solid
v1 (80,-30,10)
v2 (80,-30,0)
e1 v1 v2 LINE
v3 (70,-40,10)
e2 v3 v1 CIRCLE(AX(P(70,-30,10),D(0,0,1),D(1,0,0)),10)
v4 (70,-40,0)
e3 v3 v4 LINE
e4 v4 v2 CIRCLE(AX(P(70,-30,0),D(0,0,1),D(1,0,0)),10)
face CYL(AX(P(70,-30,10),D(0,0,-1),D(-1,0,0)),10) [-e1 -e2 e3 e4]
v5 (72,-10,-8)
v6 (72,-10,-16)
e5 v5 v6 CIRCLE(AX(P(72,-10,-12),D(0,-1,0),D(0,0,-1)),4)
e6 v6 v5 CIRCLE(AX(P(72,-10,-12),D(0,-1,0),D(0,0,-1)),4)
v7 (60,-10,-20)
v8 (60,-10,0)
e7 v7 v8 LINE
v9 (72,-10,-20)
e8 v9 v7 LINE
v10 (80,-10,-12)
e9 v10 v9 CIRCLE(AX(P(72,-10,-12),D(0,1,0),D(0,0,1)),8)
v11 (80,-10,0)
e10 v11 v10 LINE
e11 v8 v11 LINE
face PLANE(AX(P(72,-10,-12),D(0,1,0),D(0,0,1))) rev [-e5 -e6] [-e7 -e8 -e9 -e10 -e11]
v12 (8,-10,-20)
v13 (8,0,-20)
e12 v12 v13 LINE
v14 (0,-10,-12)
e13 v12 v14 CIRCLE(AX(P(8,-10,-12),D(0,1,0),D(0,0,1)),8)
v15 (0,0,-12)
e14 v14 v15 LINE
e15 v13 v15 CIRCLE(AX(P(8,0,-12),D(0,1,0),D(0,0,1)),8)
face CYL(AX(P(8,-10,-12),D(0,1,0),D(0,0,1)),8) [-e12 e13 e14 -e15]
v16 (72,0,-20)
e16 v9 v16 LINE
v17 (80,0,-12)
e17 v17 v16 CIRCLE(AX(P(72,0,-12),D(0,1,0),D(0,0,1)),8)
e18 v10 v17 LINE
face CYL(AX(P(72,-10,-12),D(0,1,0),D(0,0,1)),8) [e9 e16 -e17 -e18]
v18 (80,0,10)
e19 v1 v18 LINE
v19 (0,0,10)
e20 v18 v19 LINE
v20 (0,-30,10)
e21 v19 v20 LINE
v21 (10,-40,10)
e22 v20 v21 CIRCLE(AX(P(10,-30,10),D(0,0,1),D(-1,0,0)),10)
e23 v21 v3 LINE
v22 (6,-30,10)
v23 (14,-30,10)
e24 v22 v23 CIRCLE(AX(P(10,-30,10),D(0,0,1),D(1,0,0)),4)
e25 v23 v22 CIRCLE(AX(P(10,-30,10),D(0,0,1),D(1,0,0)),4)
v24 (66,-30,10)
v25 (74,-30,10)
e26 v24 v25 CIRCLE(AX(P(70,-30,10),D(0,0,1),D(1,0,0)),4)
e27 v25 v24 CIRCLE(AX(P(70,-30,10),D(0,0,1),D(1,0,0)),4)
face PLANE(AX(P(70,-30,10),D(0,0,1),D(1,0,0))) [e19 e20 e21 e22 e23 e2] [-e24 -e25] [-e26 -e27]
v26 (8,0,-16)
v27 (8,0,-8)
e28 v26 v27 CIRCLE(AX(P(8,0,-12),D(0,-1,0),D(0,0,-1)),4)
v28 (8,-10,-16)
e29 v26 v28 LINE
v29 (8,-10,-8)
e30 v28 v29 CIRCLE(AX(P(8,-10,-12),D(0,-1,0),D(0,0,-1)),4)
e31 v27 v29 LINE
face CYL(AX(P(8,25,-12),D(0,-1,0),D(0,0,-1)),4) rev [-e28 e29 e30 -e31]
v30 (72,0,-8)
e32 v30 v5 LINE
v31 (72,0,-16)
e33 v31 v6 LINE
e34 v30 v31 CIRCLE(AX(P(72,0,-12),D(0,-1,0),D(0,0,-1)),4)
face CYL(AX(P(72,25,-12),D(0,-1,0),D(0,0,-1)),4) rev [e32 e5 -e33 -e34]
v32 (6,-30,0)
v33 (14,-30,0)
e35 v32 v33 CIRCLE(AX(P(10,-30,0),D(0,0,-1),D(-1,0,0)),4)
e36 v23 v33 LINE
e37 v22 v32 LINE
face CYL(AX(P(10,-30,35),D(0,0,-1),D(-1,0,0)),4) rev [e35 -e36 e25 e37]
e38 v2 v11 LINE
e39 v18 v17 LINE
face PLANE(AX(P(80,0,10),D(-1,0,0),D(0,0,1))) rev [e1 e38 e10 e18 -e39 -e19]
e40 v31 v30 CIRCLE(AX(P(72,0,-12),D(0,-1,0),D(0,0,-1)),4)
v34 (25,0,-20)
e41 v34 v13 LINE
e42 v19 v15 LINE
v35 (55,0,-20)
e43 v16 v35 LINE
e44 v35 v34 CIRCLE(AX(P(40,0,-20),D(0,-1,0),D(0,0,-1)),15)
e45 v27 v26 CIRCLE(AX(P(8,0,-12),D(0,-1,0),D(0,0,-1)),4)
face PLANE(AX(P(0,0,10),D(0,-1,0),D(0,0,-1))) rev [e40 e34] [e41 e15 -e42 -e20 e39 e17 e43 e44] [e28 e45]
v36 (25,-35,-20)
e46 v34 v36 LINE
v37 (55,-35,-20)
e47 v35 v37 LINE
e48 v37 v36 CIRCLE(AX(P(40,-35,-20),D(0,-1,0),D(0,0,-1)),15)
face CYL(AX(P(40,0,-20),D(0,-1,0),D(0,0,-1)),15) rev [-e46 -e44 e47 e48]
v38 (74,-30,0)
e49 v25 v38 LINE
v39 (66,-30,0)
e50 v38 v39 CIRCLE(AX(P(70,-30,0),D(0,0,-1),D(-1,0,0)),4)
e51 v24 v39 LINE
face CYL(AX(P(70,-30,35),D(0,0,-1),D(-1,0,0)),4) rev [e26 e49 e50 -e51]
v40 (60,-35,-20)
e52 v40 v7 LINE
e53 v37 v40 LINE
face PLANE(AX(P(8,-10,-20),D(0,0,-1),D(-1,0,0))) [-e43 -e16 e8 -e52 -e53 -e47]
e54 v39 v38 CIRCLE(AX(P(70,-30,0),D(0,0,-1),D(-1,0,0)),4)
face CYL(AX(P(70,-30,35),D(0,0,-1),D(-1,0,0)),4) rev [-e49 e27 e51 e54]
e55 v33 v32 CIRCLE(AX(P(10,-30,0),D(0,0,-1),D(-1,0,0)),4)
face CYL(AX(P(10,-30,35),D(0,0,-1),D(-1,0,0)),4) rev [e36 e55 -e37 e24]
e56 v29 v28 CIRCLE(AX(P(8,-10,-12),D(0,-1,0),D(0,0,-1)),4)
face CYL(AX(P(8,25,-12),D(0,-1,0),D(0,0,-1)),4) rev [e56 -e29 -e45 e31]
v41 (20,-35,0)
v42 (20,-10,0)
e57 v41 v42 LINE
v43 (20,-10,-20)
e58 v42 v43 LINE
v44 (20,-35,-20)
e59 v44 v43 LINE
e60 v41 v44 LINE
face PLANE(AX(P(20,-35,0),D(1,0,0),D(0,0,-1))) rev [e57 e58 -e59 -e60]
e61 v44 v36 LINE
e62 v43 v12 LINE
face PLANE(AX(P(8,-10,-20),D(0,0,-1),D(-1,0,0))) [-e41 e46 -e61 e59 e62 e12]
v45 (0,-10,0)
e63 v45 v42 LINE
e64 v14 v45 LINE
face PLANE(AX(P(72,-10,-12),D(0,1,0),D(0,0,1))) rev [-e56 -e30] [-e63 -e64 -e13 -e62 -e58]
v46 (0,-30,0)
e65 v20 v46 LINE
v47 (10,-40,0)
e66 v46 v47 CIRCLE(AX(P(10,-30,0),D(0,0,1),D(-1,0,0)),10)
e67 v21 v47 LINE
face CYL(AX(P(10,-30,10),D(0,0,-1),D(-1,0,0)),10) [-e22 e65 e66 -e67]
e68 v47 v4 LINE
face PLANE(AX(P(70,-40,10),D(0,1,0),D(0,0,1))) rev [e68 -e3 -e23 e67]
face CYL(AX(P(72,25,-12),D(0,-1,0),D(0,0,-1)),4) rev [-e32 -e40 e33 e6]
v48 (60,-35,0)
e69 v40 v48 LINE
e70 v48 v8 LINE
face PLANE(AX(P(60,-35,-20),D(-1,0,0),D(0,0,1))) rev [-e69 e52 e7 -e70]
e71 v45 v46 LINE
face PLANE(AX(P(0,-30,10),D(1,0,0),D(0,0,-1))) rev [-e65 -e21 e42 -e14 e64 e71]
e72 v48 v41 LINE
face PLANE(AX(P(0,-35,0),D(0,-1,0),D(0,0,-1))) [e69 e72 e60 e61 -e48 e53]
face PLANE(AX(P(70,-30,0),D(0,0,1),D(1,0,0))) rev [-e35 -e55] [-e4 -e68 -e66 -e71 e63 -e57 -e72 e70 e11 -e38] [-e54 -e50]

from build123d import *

# Parameters (mm, degrees)
BASE_PLATE_DEPTH              = 10
LUG_FLANGE_DEPTH              = 10
SADDLE_BLOCK_DEPTH            = 25
HALF_ROUND_CRADLE_CUT_DEPTH   = 35
BASE_PLATE_LUG_HOLES_SKETCH_R = 4
BASE_PLATE_LUG_HOLES_2X_DEPTH = 35
FLANGE_LUG_HOLES_SKETCH_R     = 4
FLANGE_LUG_HOLES_2X_DEPTH     = 35


with BuildPart() as part:
    # Base Plate Sketch → Base Plate (new body)
    with BuildSketch(Plane.XY):
        with BuildLine():
            Line((0, 0), (80, 0))
            Line((80, 0), (80, -30))
            ThreePointArc((80, -30), (77.071067812, -37.071067812), (70, -40))
            Line((70, -40), (10, -40))
            ThreePointArc((10, -40), (2.928932188, -37.071067812), (0, -30))
            Line((0, -30), (0, 0))
        make_face()
    extrude(amount=BASE_PLATE_DEPTH)

    # Lug Flange Sketch → Lug Flange (add)
    with BuildSketch(Plane(origin=(0, 0, 0), x_dir=(1, 0, 0), z_dir=(0, 1, 0))):
        with BuildLine():
            Line((8, 20), (72, 20))
            ThreePointArc((72, 20), (77.656854249, 17.656854249), (80, 12))
            Line((80, 12), (80, 0))
            Line((80, 0), (0, 0))
            Line((0, 0), (0, 12))
            ThreePointArc((0, 12), (2.343145751, 17.656854249), (8, 20))
        make_face()
    extrude(amount=-LUG_FLANGE_DEPTH)

    # Saddle Block Sketch → Saddle Block (add)
    with BuildSketch(Plane.XZ.offset(10)):
        Polygon((40, 0), (60, 0), (60, -20), (20, -20), (20, 0), align=None)
    extrude(amount=SADDLE_BLOCK_DEPTH)

    # Cradle Sketch → Half-Round Cradle Cut (cut)
    with BuildSketch(Plane.XZ.offset(35)):
        with BuildLine():
            Line((25, -20), (55, -20))
            ThreePointArc((55, -20), (40, -5), (25, -20))
        make_face()
    extrude(amount=-HALF_ROUND_CRADLE_CUT_DEPTH, mode=Mode.SUBTRACT)

    # Base Plate Lug Holes Sketch → Base Plate Lug Holes 2x (cut)
    with BuildSketch(Plane(origin=(0, 0, 0), x_dir=(-1, 0, 0), z_dir=(0, 0, -1))):
        with Locations((-70, -30)):
            Circle(BASE_PLATE_LUG_HOLES_SKETCH_R)
        with Locations((-10, -30)):
            Circle(BASE_PLATE_LUG_HOLES_SKETCH_R)
    extrude(amount=-BASE_PLATE_LUG_HOLES_2X_DEPTH, mode=Mode.SUBTRACT)

    # Flange Lug Holes Sketch → Flange Lug Holes 2x (cut)
    with BuildSketch(Plane.XZ.offset(10)):
        with Locations(Location((72, -12, 0), (0, 0, 270))):
            Circle(FLANGE_LUG_HOLES_SKETCH_R)
        with Locations(Location((8, -12, 0), (0, 0, 270))):
            Circle(FLANGE_LUG_HOLES_SKETCH_R)
    extrude(amount=-FLANGE_LUG_HOLES_2X_DEPTH, mode=Mode.SUBTRACT)


solid = part.part
